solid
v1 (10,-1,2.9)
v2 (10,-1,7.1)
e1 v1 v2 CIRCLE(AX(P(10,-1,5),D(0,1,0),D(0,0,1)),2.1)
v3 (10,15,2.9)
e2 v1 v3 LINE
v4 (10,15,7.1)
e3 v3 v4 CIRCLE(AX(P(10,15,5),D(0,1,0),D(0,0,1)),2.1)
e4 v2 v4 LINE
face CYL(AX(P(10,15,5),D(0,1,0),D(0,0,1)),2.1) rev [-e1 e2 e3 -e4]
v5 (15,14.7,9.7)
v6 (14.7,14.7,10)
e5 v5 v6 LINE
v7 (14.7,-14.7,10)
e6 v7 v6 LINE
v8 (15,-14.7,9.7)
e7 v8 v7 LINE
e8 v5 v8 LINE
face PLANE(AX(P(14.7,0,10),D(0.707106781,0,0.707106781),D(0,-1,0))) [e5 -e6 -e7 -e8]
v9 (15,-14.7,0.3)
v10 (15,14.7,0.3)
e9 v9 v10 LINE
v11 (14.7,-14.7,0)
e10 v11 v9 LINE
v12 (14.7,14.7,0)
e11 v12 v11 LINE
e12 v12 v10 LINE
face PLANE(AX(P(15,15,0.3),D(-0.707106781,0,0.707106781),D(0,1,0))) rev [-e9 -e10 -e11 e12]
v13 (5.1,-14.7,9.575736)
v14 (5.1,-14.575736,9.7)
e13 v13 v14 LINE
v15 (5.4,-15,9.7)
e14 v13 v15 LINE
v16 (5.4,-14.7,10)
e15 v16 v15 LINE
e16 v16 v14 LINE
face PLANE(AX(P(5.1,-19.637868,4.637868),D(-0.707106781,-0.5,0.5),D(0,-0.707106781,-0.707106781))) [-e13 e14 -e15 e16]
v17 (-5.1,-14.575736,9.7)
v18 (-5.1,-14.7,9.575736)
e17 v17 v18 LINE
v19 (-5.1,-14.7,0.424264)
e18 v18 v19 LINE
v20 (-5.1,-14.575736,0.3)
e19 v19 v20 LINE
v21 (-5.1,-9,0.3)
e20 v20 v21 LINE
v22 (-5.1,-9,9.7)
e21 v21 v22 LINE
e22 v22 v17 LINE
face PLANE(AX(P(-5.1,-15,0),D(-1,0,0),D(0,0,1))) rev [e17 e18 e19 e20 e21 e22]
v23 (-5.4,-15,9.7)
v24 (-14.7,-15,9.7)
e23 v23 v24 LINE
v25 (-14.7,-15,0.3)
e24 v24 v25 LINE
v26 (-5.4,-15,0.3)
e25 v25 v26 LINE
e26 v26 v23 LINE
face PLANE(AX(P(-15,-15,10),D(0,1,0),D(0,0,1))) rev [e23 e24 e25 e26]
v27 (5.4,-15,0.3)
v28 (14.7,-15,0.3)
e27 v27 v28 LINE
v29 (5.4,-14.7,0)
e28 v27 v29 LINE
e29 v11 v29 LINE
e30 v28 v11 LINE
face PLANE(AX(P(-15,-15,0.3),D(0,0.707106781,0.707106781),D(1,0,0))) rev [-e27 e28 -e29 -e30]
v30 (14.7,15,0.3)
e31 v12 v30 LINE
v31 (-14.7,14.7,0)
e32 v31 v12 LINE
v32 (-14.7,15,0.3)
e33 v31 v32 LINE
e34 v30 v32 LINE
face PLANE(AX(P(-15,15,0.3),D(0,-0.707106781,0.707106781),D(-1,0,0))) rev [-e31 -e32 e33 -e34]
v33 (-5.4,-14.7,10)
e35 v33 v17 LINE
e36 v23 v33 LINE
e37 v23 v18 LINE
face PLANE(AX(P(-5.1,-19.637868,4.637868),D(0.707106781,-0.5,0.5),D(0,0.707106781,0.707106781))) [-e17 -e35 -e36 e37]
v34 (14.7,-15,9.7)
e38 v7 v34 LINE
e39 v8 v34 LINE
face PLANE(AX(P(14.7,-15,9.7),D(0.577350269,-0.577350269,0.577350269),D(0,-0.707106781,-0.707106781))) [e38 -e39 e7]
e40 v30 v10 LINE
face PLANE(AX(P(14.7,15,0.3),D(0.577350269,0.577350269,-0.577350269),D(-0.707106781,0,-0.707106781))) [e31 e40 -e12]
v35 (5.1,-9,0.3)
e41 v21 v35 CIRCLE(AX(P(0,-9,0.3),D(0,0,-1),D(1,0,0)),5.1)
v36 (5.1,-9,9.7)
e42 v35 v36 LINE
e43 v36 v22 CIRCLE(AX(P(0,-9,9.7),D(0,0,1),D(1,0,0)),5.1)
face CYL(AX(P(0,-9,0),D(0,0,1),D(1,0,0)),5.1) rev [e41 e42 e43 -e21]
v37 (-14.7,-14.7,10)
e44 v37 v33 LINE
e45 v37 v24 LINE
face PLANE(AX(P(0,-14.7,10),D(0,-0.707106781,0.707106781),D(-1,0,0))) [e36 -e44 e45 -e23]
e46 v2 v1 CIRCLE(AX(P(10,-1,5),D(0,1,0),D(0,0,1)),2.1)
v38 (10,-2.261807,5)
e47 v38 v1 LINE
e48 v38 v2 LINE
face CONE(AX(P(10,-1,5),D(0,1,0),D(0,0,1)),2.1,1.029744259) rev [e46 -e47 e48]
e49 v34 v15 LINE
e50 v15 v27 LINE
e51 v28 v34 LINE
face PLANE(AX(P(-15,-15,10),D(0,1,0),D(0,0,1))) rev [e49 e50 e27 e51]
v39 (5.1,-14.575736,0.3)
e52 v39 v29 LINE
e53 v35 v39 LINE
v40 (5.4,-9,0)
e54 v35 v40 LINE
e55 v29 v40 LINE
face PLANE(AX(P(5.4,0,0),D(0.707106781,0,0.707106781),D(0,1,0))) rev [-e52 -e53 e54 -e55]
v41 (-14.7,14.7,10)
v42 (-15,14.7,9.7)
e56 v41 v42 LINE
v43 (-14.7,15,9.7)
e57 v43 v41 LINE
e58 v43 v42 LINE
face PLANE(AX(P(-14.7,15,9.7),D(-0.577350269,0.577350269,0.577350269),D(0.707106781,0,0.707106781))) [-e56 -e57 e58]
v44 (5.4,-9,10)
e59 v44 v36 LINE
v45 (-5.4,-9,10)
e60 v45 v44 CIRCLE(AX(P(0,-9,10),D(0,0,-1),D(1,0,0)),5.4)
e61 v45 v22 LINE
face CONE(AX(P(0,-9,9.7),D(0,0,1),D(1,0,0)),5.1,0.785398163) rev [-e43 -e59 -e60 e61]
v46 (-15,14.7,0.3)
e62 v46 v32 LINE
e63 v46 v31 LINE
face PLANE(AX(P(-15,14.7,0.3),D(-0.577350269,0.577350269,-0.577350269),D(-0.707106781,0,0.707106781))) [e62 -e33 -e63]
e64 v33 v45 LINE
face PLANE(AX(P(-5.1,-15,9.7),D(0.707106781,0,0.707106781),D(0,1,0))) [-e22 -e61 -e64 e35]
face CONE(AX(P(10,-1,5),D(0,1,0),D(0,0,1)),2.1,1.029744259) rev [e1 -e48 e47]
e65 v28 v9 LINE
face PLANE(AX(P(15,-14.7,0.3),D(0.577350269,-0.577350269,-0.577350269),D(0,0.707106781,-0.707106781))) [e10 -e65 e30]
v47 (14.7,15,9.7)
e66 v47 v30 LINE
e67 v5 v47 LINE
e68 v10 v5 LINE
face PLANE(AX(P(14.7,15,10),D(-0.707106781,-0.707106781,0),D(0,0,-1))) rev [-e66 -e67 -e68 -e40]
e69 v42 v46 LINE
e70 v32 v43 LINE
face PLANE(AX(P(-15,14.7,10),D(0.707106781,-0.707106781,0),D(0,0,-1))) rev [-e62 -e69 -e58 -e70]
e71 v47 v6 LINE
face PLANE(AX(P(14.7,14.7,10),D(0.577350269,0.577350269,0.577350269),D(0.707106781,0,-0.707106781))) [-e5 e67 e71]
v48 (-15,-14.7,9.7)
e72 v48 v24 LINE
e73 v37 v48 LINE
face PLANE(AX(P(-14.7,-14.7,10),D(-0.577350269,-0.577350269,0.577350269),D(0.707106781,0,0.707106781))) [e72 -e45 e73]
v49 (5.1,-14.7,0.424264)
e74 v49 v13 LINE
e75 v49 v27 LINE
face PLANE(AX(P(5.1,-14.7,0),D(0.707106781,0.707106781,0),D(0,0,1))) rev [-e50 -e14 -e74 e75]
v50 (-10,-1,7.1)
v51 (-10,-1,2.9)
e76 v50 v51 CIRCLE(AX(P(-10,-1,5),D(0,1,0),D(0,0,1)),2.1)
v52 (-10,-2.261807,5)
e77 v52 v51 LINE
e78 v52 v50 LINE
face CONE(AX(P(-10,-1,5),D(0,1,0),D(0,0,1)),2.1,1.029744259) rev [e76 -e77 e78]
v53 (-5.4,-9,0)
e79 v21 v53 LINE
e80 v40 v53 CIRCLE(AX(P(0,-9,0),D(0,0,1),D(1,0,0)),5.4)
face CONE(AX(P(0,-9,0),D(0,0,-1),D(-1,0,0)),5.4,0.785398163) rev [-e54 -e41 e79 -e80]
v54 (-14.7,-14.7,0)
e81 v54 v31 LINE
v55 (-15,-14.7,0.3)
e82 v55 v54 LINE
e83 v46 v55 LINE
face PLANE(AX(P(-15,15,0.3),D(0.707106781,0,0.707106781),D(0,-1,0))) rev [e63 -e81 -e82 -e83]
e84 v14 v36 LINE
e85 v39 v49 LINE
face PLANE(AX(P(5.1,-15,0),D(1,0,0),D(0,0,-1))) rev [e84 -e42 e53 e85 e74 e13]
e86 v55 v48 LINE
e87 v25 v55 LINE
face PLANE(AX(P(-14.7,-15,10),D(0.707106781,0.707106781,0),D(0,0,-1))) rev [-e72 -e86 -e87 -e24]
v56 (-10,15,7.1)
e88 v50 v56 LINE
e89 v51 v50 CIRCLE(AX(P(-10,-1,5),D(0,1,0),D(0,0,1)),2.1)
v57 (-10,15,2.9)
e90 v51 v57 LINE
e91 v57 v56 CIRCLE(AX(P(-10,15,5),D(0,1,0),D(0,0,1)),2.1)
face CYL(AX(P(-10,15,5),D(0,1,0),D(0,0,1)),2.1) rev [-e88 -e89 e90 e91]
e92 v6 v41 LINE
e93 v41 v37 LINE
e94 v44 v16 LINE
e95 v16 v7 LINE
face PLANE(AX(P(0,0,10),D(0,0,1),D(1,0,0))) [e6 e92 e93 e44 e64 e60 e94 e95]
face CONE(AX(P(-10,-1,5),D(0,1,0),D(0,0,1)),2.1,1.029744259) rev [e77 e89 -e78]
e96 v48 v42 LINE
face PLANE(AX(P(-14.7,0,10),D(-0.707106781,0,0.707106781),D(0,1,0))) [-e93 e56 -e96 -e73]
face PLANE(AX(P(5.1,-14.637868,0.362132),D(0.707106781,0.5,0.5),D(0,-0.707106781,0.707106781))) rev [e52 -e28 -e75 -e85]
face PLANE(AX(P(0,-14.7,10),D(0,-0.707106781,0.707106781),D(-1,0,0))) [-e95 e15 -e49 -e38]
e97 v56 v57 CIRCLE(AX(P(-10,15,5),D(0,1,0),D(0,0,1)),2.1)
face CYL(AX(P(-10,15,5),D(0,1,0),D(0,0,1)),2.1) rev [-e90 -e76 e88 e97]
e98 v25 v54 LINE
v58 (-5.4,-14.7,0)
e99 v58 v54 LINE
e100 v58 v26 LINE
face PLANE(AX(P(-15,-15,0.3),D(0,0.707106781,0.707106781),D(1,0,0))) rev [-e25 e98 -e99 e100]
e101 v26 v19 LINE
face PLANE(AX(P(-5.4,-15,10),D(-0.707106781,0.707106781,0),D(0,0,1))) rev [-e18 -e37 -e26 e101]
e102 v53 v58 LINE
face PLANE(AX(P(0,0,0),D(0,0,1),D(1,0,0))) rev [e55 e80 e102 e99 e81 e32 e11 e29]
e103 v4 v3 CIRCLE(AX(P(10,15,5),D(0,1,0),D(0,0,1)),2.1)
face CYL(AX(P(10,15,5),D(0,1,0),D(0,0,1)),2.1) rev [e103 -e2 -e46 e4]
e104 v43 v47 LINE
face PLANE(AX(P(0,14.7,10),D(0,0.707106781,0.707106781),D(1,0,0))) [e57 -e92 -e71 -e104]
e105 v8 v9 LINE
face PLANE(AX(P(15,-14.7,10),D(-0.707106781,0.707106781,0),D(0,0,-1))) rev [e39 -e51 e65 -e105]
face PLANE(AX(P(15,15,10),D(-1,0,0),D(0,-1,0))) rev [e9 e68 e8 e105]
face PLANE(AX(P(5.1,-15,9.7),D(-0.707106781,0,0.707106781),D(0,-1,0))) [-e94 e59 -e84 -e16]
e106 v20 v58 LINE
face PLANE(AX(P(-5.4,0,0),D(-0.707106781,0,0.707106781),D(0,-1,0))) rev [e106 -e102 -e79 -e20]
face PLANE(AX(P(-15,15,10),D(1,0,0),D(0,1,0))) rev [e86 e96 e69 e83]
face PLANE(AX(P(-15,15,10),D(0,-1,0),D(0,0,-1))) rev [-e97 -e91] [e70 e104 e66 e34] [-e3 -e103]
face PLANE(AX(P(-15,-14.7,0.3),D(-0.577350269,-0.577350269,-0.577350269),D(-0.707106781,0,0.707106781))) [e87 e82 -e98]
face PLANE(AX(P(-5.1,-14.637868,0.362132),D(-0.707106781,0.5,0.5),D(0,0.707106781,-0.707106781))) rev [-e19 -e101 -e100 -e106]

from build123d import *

# Parameters (mm, degrees)
SKETCH_1_W             = 30
SKETCH_1_H             = 30
EXTRUDE_1_DEPTH        = 10
HOLE_WIZARD_M5_1_D     = 4.2
HOLE_WIZARD_M5_1_DEPTH = 16
HOLE_WIZARD_M5_1_TIP   = 1.2618073
CHAMFER_1_SIZE         = 0.3
CUT_EXTRUDE_1_DEPTH    = 24.452078799
CHAMFER_2_SIZE         = 0.3


with BuildPart() as part:
    # 草图1 → 凸台-拉伸1 (new body)
    with BuildSketch(Plane.XY):
        Rectangle(SKETCH_1_W, SKETCH_1_H)
    extrude(amount=EXTRUDE_1_DEPTH)

    # M5 螺纹孔1
    with Locations(Plane(origin=(9.101151333, 15, -0.360612024), x_dir=(-1, 0, 0), z_dir=(0, 1, 0))):
        with Locations((-0.898848667, 5.360612024), (19.101151333, 5.360612024)):
            Hole(HOLE_WIZARD_M5_1_D / 2, depth=HOLE_WIZARD_M5_1_DEPTH)
            with Locations((0, 0, -(HOLE_WIZARD_M5_1_DEPTH + HOLE_WIZARD_M5_1_TIP / 2))):  # 118° drill point
                Cone(0, HOLE_WIZARD_M5_1_D / 2, HOLE_WIZARD_M5_1_TIP, mode=Mode.SUBTRACT)

    # 倒角1
    chamfer_1_edges = [part.edges().sort_by_distance(p)[0] for p in [
        (-15, 0, 10),
        (0, -15, 10),
        (15, 0, 10),
        (0, -15, 0),
        (-15, 0, 0),
        (0, 15, 0),
        (15, 0, 0),
        (0, 15, 10),
        (15, -15, 5),
        (-15, -15, 5),
        (-15, 15, 5),
        (15, 15, 5),
    ]]
    chamfer(chamfer_1_edges, length=CHAMFER_1_SIZE)

    # 草图4 → 切除-拉伸1 (cut, through all)
    with BuildSketch(Plane.XY.offset(10)):
        with BuildLine():
            Line((-5.1, -15), (-5.1, -9))
            ThreePointArc((-5.1, -9), (0, -3.9), (5.1, -9))
            Line((5.1, -9), (5.1, -15))
            ThreePointArc((5.1, -15), (0, -20.1), (-5.1, -15))
        make_face()
    extrude(amount=-CUT_EXTRUDE_1_DEPTH, mode=Mode.SUBTRACT)

    # 倒角2
    chamfer_2_edges = [part.edges().sort_by_distance(p)[0] for p in [
        (5.1, -14.85, 0.15),
        (-5.1, -14.85, 0.15),
        (-5.1, -14.85, 9.85),
        (5.1, -14.85, 9.85),
        (5.1, -15, 5),
        (-5.1, -11.85, 0),
        (-5.1, -15, 5),
        (0, -3.9, 0),
        (5.1, -11.85, 0),
        (5.1, -11.85, 10),
        (0, -3.9, 10),
        (-5.1, -11.85, 10),
    ]]
    chamfer(chamfer_2_edges, length=CHAMFER_2_SIZE)


solid = part.part
